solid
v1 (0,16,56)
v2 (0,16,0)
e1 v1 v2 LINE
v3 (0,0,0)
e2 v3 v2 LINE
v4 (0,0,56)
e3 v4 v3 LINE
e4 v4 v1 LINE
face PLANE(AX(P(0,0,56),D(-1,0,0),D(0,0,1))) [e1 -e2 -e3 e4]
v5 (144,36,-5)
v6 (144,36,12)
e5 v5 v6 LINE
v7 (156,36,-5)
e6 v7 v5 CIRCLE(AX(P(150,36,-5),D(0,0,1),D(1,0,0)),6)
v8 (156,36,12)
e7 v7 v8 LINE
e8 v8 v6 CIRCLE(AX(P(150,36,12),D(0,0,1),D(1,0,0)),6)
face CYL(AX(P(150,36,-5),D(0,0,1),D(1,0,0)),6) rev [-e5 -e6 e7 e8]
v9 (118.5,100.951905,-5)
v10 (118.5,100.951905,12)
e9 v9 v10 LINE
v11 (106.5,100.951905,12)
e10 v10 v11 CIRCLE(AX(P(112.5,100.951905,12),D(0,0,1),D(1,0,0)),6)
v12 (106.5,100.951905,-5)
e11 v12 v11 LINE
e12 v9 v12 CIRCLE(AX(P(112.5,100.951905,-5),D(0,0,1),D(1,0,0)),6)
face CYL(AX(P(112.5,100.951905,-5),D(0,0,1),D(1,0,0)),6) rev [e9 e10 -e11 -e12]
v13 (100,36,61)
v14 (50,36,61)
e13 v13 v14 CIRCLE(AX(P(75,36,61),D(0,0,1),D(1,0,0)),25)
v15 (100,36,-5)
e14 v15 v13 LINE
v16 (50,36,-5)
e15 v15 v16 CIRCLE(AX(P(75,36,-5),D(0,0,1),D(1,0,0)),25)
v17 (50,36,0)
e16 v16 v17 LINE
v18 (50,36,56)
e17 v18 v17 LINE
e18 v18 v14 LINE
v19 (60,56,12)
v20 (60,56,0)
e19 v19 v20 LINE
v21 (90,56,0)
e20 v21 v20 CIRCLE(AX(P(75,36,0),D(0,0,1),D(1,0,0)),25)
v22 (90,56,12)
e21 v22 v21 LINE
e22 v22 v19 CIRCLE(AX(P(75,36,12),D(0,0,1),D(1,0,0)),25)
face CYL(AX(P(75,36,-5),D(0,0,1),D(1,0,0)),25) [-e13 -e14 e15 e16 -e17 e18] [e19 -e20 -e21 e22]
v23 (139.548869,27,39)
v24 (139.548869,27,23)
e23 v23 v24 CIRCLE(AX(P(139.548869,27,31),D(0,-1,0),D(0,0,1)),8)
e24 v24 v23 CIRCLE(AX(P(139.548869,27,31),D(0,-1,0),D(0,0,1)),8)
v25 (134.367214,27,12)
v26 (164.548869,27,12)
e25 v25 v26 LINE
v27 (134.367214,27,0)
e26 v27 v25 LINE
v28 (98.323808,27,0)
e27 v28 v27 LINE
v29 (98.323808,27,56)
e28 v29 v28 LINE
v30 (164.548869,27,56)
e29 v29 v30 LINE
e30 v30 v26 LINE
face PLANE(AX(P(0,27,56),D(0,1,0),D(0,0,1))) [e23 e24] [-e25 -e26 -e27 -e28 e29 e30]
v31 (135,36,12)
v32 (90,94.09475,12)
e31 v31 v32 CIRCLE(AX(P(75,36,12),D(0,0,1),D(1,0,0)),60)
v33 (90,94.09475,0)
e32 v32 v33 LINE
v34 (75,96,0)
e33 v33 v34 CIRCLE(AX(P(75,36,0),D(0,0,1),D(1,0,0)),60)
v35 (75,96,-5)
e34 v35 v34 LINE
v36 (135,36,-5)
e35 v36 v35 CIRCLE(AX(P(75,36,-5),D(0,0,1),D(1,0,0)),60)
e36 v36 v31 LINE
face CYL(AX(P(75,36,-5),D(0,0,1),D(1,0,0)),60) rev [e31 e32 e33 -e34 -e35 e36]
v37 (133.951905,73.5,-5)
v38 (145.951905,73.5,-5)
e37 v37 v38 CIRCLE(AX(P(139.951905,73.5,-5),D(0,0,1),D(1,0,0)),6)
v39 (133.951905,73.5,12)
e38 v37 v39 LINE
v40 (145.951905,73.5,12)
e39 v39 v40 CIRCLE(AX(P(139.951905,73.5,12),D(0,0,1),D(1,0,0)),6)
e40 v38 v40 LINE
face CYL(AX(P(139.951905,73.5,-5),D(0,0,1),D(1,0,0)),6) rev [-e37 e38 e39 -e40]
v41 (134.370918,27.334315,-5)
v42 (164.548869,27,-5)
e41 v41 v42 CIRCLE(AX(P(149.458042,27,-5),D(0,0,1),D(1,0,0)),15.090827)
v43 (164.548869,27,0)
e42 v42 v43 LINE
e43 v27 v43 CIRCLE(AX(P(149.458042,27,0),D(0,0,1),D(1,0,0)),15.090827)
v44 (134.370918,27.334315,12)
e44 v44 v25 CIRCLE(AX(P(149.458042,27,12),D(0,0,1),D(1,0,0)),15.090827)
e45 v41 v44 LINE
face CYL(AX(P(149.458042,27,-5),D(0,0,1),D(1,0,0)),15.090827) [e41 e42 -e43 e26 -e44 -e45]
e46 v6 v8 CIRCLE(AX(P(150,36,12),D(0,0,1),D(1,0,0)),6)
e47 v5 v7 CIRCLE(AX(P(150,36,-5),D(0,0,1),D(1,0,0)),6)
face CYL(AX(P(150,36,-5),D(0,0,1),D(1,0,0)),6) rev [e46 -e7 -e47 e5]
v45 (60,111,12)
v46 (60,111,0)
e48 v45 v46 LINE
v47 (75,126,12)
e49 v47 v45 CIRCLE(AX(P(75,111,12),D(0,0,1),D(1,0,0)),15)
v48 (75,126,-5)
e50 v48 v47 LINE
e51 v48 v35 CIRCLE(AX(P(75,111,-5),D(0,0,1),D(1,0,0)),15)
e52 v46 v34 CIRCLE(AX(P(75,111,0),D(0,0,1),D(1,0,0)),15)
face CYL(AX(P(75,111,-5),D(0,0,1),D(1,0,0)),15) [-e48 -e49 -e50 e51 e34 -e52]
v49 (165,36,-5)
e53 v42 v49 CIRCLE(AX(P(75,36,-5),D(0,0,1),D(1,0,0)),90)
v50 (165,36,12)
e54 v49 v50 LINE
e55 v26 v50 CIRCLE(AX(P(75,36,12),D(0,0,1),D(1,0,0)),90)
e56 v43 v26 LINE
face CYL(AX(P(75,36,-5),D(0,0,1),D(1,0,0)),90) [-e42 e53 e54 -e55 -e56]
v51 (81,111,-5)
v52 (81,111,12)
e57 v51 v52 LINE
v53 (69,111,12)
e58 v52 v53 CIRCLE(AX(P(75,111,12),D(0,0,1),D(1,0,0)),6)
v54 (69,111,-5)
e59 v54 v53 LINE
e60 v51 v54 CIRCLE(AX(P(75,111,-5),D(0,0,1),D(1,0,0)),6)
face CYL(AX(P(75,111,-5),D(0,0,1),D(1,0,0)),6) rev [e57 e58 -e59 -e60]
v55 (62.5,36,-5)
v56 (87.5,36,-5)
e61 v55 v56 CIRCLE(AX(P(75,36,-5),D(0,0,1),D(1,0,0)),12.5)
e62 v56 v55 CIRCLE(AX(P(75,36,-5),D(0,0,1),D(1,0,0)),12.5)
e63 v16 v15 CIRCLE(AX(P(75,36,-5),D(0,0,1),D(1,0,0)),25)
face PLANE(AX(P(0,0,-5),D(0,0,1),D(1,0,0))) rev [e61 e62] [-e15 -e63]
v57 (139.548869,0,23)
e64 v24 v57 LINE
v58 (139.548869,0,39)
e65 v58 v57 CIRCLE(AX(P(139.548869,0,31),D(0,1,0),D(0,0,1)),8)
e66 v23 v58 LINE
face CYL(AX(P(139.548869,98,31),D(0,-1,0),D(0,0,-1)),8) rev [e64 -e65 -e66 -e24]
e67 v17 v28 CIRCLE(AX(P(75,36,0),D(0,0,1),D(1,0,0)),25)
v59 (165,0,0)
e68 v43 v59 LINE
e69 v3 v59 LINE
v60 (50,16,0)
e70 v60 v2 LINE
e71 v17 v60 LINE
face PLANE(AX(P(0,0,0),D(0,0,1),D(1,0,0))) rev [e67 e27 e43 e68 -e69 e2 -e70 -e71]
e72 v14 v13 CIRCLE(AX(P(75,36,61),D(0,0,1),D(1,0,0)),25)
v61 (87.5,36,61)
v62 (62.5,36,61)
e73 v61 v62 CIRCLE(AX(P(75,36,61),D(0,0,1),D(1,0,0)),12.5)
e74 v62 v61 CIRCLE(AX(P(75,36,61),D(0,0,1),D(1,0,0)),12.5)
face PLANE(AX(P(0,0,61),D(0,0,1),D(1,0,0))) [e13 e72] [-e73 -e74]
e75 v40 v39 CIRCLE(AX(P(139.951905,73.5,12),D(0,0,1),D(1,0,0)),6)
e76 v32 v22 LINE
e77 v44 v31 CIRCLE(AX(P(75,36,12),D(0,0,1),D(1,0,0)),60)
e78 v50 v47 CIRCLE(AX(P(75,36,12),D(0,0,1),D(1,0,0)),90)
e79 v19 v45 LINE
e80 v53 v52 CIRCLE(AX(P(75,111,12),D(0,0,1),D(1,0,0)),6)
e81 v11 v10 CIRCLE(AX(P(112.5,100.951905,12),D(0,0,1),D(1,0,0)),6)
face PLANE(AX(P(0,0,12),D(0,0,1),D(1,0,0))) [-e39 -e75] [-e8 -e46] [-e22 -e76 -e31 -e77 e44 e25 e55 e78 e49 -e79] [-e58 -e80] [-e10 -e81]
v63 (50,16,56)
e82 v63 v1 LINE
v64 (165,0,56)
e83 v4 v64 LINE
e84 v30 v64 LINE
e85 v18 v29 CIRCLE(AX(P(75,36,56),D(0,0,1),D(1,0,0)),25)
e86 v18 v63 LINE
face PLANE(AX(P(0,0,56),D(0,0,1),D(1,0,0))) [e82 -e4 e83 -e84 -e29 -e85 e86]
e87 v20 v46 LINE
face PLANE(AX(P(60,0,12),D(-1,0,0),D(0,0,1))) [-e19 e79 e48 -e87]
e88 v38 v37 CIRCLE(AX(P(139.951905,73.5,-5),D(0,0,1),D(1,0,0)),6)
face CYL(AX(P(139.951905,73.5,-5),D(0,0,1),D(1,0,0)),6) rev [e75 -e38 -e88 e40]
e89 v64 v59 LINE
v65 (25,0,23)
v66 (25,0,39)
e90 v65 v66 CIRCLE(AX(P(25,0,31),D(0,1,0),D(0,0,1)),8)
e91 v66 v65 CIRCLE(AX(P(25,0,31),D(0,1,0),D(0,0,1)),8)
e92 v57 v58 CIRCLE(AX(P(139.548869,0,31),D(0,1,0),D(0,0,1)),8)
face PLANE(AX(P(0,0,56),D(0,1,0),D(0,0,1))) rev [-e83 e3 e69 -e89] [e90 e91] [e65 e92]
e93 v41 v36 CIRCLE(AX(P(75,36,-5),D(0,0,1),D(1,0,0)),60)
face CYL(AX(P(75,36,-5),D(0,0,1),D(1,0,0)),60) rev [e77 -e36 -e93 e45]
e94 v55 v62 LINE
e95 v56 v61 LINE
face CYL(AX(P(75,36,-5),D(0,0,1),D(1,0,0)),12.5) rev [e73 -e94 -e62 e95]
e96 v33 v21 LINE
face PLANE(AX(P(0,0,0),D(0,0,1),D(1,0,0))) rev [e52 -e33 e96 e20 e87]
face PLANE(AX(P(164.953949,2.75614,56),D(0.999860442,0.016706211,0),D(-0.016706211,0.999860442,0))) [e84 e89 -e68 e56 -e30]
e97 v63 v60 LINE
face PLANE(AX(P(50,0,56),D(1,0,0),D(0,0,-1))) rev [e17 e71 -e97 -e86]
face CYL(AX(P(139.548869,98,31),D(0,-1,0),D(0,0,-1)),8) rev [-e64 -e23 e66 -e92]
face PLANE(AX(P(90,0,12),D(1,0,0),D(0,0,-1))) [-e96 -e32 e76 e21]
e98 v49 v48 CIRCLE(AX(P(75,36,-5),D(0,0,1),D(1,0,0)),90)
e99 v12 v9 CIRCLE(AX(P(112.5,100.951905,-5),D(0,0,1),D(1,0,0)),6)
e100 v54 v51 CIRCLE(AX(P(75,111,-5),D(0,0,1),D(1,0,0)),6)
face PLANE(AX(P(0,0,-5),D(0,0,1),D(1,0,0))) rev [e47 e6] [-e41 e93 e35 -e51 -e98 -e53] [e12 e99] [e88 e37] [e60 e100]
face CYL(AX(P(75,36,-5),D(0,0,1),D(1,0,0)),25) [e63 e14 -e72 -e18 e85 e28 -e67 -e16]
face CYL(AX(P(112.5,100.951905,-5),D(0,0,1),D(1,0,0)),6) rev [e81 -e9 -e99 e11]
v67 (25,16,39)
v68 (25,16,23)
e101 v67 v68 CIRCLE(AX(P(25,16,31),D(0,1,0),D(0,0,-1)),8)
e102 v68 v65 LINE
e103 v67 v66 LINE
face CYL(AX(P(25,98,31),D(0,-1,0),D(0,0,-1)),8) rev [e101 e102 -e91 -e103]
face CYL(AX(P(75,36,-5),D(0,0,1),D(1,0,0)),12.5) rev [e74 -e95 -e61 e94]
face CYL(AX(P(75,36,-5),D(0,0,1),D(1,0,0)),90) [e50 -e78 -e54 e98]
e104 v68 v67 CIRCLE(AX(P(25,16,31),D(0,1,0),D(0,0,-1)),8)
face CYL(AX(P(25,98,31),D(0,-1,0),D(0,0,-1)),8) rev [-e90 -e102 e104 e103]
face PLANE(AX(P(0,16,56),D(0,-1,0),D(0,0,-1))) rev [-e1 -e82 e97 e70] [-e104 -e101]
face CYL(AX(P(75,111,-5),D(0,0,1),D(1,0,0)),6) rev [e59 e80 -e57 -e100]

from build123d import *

# Parameters (mm, degrees)
STEPPED_BASE_BLOCK_DEPTH           = 61
STEPPED_BASE_BLOCK_DEPTH_BACK      = 5
BRACKET_PROFILE_SKETCH_R           = 25
BRACKET_PROFILE_SKETCH_R_2         = 12.5
BEARING_BOSS_DEPTH                 = 56
QUADRANT_MOUNTING_PLATE_DEPTH      = 12
QUADRANT_MOUNTING_PLATE_DEPTH_BACK = 5
SKETCH1_9_R                        = 6
UPRIGHT_WEB_DEPTH                  = 12
BASE_HOLES_SKETCH_R                = 8
BASE_THROUGH_HOLES_DEPTH           = 98


with BuildPart() as part:
    # Bracket Profile Sketch → Stepped Base Block (new, two sides: drawn at the far end of the back side and taken through both)
    with BuildSketch(Plane.XY.offset(-STEPPED_BASE_BLOCK_DEPTH_BACK)):
        with Locations((75, 36)):
            Circle(BRACKET_PROFILE_SKETCH_R)
        with Locations((75, 36)):
            Circle(BRACKET_PROFILE_SKETCH_R_2, mode=Mode.SUBTRACT)
    extrude(amount=STEPPED_BASE_BLOCK_DEPTH + STEPPED_BASE_BLOCK_DEPTH_BACK)

    # Sketch1_5 → Bearing Boss (add)
    with BuildSketch(Plane.XY):
        with BuildLine():
            Line((0, 16), (0, 0))
            Line((0, 0), (75, 0))
            Line((75, 0), (165, 0))
            Line((165, 0), (164.54886934, 27))
            ThreePointArc((164.54886934, 27), (149.458041876, 11.909172536), (134.367214412, 27))
            Line((134.367214412, 27), (134.3211598, 27))
            Line((134.3211598, 27), (98.323807579, 27))
            ThreePointArc((98.323807579, 27), (70.422620263, 11.422620263), (50, 36))
            Line((50, 36), (50, 16))
            Line((50, 16), (0, 16))
        make_face()
        with BuildLine():
            ThreePointArc((134.367214412, 27), (149.458041876, 11.909172536), (164.54886934, 27))
            Line((164.54886934, 27), (134.367214412, 27))
        make_face()
    extrude(amount=BEARING_BOSS_DEPTH)

    # Sketch1_9 → Quadrant Mounting Plate (add, two sides: drawn at the far end of the back side and taken through both)
    # profile 1 of 2: a face of its own
    with BuildSketch(Plane.XY.offset(-QUADRANT_MOUNTING_PLATE_DEPTH_BACK)):
        with BuildLine():
            Line((134.367214412, 27), (164.54886934, 27))
            ThreePointArc((164.54886934, 27), (141.745786384, 96.373835392), (75, 126))
            ThreePointArc((75, 126), (64.393398282, 121.606601718), (60, 111))
            ThreePointArc((60, 111), (64.393398282, 100.393398282), (75, 96))
            ThreePointArc((75, 96), (82.560257549, 95.521781776), (90, 94.094750193))
            ThreePointArc((90, 94.094750193), (124.13637209, 70.432788703), (134.725771353, 30.270057917))
            ThreePointArc((134.725771353, 30.270057917), (134.566433501, 28.8), (134.370917994, 27.334315001))
            ThreePointArc((134.370917994, 27.334315001), (134.368140336, 27.167167757), (134.367214412, 27))
        make_face()
        with Locations((150, 36)):
            Circle(SKETCH1_9_R, mode=Mode.SUBTRACT)
        with Locations((75, 111)):
            Circle(SKETCH1_9_R, mode=Mode.SUBTRACT)
        with Locations((139.951905284, 73.5)):
            Circle(SKETCH1_9_R, mode=Mode.SUBTRACT)
        with Locations((112.5, 100.951905284)):
            Circle(SKETCH1_9_R, mode=Mode.SUBTRACT)
    # profile 2 of 2: a face of its own
    with BuildSketch(Plane.XY.offset(-QUADRANT_MOUNTING_PLATE_DEPTH_BACK)):
        with BuildLine():
            ThreePointArc((134.367214412, 27), (149.458041876, 11.909172536), (164.54886934, 27))
            Line((164.54886934, 27), (134.367214412, 27))
        make_face()
    extrude(amount=QUADRANT_MOUNTING_PLATE_DEPTH + QUADRANT_MOUNTING_PLATE_DEPTH_BACK)

    # Sketch1_10 → Upright Web (add)
    with BuildSketch(Plane.XY):
        with BuildLine():
            Line((60, 61), (60, 56))
            ThreePointArc((60, 56), (75, 61), (90, 56))
            Line((90, 56), (90, 61))
            Line((90, 61), (90, 94.094750193))
            ThreePointArc((90, 94.094750193), (82.560257549, 95.521781776), (75, 96))
            ThreePointArc((75, 96), (64.393398282, 100.393398282), (60, 111))
            Line((60, 111), (60, 96))
            Line((60, 96), (60, 61))
        make_face()
    extrude(amount=UPRIGHT_WEB_DEPTH)

    # Base Holes Sketch → Base Through Holes (cut)
    with BuildSketch(Plane(origin=(0, 0, 0), x_dir=(1, 0, 0), z_dir=(0, 1, 0))):
        with Locations(Location((25, -31, 0), (0, 0, 90))):
            Circle(BASE_HOLES_SKETCH_R)
        with Locations(Location((139.54886934, -31, 0), (0, 0, 270))):
            Circle(BASE_HOLES_SKETCH_R)
    extrude(amount=BASE_THROUGH_HOLES_DEPTH, mode=Mode.SUBTRACT)


solid = part.part
